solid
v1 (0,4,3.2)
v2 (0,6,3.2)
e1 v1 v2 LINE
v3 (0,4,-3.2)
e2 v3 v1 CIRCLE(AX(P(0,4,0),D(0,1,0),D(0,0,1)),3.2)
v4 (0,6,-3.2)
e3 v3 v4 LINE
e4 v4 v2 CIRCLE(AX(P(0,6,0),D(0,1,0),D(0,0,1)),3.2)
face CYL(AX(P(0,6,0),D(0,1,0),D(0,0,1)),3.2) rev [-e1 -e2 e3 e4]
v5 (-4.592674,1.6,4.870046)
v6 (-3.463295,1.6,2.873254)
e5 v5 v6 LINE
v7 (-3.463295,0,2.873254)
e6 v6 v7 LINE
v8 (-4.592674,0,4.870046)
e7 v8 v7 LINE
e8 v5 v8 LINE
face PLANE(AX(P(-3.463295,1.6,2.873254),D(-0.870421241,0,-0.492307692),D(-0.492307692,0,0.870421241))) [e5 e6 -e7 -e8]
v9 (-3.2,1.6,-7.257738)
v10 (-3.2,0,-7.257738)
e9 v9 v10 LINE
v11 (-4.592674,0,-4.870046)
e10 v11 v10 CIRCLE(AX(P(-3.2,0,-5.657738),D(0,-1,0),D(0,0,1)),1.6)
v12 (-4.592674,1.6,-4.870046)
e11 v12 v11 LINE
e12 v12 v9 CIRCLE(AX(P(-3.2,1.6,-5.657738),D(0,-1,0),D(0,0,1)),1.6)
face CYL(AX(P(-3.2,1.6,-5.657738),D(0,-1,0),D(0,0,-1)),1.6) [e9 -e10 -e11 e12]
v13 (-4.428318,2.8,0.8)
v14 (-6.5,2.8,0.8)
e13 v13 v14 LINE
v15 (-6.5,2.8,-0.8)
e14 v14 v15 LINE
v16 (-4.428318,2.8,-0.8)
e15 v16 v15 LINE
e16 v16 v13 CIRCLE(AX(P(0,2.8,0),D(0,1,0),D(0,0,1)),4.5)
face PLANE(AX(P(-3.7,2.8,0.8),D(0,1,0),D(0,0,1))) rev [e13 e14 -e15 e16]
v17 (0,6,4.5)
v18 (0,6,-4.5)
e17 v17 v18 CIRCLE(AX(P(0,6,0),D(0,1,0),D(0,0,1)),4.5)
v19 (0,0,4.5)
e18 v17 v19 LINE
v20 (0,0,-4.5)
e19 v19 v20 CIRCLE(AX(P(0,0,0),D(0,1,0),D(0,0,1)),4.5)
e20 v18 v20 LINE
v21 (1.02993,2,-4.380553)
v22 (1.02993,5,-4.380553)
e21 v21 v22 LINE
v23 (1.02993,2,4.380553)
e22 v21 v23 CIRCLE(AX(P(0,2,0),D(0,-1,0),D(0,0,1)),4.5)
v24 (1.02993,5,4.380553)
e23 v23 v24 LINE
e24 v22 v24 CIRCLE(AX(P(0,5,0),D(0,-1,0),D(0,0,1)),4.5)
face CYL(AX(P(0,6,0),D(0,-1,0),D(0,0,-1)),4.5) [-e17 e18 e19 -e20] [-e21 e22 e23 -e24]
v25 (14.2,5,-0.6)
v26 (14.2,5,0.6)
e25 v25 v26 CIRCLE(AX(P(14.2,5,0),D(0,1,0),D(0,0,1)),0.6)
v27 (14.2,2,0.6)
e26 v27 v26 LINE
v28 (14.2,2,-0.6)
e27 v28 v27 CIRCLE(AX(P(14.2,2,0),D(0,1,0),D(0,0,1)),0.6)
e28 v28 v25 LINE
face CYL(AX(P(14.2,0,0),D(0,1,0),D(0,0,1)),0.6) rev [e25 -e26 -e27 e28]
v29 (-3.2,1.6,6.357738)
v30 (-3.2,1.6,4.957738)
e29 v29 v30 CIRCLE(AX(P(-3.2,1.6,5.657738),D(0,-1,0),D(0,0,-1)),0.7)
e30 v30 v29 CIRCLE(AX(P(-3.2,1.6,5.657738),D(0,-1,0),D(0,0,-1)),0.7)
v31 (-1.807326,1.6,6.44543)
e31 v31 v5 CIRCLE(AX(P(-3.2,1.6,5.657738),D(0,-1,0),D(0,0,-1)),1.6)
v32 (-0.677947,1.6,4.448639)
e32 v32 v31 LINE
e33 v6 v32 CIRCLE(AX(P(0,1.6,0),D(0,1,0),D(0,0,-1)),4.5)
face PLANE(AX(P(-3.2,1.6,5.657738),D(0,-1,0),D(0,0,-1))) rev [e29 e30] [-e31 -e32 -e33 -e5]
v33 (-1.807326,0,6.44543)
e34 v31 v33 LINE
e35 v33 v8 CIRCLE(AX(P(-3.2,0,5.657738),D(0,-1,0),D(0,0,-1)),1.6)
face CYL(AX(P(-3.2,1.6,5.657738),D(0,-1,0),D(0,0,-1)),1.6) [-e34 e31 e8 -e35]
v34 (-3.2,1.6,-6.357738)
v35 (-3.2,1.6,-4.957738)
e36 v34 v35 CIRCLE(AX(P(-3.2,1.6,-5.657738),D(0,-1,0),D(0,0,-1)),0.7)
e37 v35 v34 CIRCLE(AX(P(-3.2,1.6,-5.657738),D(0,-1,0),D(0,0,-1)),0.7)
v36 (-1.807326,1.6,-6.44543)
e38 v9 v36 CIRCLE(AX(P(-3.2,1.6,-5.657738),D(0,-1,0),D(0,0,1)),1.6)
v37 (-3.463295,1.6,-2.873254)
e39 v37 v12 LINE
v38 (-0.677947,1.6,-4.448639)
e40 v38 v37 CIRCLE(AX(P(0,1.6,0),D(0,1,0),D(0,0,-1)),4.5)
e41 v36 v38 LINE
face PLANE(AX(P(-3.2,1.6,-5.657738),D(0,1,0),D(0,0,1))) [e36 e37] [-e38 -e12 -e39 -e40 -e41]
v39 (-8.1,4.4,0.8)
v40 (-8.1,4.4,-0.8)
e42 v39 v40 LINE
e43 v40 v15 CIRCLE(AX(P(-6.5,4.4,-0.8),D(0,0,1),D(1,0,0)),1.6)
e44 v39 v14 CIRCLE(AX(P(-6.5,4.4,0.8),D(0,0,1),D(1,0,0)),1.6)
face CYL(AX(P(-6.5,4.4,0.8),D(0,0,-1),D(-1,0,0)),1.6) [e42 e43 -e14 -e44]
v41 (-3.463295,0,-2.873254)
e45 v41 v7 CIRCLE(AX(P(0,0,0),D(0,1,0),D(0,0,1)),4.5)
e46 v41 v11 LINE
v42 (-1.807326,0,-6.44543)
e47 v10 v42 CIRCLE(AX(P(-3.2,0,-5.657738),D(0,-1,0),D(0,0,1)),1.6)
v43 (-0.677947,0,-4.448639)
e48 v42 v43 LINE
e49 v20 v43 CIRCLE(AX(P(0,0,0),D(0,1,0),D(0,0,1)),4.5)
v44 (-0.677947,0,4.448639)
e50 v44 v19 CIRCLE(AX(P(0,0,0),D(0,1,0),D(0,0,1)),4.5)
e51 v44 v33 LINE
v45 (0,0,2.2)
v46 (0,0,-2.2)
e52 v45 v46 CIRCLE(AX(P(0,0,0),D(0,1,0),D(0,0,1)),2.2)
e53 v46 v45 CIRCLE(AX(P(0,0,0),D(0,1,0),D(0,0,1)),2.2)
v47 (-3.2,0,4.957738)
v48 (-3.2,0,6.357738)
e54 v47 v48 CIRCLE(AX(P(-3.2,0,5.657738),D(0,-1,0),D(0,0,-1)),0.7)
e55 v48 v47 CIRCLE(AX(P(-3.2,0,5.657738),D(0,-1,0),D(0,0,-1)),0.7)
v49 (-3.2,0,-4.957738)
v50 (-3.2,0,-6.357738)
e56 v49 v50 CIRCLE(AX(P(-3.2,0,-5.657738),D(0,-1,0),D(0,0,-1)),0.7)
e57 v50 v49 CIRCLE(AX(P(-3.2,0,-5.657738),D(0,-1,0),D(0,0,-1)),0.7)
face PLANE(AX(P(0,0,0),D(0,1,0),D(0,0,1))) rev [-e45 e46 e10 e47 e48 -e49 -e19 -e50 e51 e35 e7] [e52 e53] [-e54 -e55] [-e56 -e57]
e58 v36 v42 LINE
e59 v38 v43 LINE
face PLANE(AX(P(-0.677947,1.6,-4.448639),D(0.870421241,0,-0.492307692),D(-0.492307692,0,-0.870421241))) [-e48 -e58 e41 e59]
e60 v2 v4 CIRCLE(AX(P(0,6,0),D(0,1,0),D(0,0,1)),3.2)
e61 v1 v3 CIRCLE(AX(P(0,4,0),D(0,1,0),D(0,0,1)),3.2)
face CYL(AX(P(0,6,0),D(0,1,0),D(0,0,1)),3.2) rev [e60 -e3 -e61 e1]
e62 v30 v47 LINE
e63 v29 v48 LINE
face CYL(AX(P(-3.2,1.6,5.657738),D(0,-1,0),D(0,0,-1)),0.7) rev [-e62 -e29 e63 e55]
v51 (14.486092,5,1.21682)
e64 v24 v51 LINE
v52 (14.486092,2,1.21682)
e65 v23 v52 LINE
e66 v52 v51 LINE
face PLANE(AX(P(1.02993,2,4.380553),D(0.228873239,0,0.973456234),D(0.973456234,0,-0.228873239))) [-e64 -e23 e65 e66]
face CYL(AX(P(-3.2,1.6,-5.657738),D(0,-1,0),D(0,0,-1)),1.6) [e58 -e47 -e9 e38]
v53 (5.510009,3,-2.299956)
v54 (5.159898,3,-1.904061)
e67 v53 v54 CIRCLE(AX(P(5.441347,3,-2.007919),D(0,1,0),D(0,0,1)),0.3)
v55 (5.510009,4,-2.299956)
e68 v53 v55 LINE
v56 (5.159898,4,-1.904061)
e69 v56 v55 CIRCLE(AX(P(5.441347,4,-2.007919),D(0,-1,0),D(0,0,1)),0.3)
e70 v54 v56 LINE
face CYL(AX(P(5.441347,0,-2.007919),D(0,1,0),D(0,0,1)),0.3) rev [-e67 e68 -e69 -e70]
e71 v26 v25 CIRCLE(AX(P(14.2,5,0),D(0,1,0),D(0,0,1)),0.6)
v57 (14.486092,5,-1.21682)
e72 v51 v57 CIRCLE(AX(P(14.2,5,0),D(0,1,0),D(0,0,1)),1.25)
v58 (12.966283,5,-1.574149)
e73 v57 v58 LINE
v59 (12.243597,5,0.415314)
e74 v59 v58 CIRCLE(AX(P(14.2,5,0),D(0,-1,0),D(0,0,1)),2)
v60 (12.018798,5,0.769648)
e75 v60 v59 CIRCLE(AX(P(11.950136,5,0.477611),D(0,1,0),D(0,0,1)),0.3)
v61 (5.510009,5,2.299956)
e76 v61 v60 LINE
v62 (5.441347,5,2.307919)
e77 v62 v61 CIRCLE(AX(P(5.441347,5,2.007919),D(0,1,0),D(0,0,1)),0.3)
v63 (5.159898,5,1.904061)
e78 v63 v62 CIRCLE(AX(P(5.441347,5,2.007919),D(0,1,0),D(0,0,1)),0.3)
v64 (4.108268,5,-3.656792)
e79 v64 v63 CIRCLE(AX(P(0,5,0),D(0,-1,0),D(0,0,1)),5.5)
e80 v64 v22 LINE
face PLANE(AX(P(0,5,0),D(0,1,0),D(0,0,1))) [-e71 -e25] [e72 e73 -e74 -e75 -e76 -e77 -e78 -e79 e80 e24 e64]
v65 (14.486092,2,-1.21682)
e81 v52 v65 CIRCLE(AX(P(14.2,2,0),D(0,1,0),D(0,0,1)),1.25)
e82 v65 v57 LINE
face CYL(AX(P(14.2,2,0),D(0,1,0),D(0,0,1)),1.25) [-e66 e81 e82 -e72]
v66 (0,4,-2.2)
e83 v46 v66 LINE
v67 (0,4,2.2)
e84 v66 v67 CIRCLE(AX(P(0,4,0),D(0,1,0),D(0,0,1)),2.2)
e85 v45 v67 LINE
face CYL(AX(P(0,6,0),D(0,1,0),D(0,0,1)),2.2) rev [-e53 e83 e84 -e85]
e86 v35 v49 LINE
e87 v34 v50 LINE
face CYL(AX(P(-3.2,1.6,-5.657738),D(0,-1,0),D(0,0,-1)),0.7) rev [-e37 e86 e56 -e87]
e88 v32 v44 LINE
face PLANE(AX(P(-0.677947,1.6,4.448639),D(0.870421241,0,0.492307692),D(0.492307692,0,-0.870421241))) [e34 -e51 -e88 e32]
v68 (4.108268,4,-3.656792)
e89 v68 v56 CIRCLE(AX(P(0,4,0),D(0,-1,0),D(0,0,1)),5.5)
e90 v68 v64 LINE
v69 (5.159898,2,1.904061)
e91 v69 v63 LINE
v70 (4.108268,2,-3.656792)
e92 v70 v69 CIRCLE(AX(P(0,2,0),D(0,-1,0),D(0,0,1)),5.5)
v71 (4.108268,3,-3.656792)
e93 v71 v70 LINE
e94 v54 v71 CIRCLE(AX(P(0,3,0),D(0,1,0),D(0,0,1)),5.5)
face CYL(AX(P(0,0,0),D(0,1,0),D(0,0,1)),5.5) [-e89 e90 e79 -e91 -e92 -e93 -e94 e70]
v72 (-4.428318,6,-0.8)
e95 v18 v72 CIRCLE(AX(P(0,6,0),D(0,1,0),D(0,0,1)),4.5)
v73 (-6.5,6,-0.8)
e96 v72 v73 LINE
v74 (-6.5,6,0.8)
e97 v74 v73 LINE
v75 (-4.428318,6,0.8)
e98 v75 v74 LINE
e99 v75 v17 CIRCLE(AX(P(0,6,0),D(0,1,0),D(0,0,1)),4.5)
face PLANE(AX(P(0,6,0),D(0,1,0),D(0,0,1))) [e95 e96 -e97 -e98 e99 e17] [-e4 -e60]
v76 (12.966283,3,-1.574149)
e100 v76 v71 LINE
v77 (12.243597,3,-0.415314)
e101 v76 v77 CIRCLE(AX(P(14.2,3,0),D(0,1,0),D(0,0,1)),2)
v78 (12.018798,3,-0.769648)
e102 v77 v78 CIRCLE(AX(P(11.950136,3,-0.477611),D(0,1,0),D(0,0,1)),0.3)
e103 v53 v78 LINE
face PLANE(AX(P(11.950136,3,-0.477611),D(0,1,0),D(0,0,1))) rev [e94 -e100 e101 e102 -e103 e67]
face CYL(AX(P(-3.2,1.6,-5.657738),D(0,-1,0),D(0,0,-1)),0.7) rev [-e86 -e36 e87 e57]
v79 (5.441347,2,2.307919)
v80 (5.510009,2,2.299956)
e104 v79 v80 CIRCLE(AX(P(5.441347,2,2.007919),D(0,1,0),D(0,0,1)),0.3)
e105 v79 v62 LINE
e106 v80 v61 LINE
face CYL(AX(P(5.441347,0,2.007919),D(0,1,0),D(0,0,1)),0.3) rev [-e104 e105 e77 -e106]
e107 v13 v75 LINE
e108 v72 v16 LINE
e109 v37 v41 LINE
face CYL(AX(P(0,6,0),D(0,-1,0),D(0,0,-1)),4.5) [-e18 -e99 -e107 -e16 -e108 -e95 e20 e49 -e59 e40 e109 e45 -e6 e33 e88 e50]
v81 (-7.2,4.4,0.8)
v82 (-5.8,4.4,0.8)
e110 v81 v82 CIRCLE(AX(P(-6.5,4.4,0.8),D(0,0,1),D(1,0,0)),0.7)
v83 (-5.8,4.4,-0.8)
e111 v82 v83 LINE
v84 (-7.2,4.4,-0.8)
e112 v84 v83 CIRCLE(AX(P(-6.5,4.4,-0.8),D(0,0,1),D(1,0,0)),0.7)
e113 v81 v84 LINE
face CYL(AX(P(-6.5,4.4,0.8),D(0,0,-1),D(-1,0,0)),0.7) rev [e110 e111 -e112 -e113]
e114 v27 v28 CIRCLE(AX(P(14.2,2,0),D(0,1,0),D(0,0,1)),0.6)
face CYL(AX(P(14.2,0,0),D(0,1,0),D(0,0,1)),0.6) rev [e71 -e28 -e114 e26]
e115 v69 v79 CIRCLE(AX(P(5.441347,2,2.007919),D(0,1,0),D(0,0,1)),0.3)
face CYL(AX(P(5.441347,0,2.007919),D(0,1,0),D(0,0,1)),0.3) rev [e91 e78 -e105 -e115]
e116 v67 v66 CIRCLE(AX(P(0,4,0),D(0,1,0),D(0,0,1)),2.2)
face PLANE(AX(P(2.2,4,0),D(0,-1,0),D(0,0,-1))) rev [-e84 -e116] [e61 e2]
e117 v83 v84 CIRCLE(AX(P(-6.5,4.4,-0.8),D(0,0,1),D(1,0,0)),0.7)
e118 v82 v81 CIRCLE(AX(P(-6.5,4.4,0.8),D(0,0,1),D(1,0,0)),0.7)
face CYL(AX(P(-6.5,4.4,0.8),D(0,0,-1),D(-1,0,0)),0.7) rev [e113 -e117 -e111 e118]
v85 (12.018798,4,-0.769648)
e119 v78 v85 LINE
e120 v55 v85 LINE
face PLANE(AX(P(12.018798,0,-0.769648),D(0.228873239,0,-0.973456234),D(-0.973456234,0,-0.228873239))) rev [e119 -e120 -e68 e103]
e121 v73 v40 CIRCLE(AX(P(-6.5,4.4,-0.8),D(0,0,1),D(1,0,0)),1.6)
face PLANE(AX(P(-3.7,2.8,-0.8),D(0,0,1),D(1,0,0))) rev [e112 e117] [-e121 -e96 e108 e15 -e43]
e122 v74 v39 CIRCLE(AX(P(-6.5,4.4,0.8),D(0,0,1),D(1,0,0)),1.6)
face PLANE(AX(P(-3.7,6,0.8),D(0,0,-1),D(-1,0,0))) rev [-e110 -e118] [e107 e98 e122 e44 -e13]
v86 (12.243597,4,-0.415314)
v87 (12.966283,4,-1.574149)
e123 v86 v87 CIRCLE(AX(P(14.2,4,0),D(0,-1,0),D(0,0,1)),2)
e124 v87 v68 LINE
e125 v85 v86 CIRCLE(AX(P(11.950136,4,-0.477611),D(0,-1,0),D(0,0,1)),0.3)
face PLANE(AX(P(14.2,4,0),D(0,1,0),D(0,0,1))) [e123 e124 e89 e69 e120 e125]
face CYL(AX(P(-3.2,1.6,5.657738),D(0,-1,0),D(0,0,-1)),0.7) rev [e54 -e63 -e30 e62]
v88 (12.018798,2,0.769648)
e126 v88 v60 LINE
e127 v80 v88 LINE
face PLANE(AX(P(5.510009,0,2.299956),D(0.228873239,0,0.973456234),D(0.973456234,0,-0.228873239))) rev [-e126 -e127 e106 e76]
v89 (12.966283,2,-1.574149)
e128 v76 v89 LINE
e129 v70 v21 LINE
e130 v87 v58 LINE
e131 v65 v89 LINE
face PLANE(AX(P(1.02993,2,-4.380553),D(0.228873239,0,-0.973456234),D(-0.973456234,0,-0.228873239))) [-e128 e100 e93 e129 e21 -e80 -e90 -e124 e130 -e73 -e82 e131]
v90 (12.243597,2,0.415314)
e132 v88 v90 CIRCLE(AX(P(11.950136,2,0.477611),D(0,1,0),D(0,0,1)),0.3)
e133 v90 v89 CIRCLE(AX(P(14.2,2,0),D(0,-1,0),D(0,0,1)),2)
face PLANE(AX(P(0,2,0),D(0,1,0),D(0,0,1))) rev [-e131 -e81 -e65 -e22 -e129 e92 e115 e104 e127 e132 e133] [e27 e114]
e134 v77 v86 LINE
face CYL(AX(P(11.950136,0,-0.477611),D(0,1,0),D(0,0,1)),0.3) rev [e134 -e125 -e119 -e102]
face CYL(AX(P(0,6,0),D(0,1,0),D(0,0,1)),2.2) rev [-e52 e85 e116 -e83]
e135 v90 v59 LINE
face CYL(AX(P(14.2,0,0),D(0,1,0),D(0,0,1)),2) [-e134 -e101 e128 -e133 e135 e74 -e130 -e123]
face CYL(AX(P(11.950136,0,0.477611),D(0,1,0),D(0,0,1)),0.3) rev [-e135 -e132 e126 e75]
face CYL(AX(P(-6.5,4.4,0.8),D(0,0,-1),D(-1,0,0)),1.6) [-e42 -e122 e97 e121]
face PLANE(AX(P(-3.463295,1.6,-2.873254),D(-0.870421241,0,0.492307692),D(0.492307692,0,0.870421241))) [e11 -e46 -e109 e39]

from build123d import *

# Parameters (mm, degrees)
HUB_PROFILE_SKETCH_R           = 4.5
HUB_CYLINDER_DEPTH             = 6
ARM_START                      = -4
ARM_DEPTH                      = 3
FLAT_EAR_PROFILE_SKETCH_R      = 0.7
FLAT_MOUNTING_EAR_DEPTH        = 1.6
UPRIGHT_EAR_PROFILE_SKETCH_R   = 0.7
UPRIGHT_MOUNTING_EAR_DEPTH     = 0.8
UPRIGHT_EAR_EXTENSION_SKETCH_W = 1.6
UPRIGHT_EAR_EXTENSION_SKETCH_H = 3.2
UPRIGHT_EAR_EXTENSION_DEPTH    = 0.8
HUB_BORE_CBORE_4_4_D           = 4.4
HUB_BORE_CBORE_4_4_DEPTH       = 100
HUB_BORE_CBORE_4_4_CBORE_D     = 6.4
HUB_BORE_CBORE_4_4_CBORE_DEPTH = 2
ARM_FRAME_CUT_DEPTH            = 18.786996987
ARM_FRAME_CUT_DEPTH_BACK       = 18.786996987
ARM_FRAME_CUT_SKETCH_R         = 0.6
ARM_START_2                    = -1
ARM_WINDOW_CUT_A_DEPTH         = 1
ARM_START_3                    = -3
ARM_WINDOW_CUT_B_DEPTH         = 1


with BuildPart() as part:
    # Hub Profile Sketch → Hub Cylinder (new body)
    with BuildSketch(Plane(origin=(0, 0, 0), x_dir=(1, 0, 0), z_dir=(0, 1, 0))):
        with Locations(Location((0, 0, 0), (0, 0, 270))):
            Circle(HUB_PROFILE_SKETCH_R)
    extrude(amount=HUB_CYLINDER_DEPTH)

    # Arm Profile Sketch → Arm (add)
    with BuildSketch(Plane(origin=(0, 6, 0), x_dir=(1, 0, 0), z_dir=(0, 1, 0)).offset(ARM_START)):
        with BuildLine():
            Line((1.029929577, 4.380553055), (14.486091549, 1.216820293))
            ThreePointArc((14.486091549, 1.216820293), (15.45, 0), (14.486091549, -1.216820293))
            Line((14.486091549, -1.216820293), (1.029929577, -4.380553055))
            ThreePointArc((1.029929577, -4.380553055), (4.5, 0), (1.029929577, 4.380553055))
        make_face()
    extrude(amount=ARM_DEPTH)

    # Flat Ear Profile Sketch → Flat Mounting Ear (add)
    # profile 1 of 2: a face of its own
    with BuildSketch(Plane.XZ):
        with BuildLine():
            Line((-0.677946652, 4.448638931), (-1.807326015, 6.445430372))
            ThreePointArc((-1.807326015, 6.445430372), (-3.987692308, 7.050412049), (-4.592673985, 4.870045756))
            Line((-4.592673985, 4.870045756), (-3.463294622, 2.873254315))
            ThreePointArc((-3.463294622, 2.873254315), (-2.215384615, 3.916895583), (-0.677946652, 4.448638931))
        make_face()
        with Locations(Location((-3.2, 5.657738064, 0), (0, 0, 270))):
            Circle(FLAT_EAR_PROFILE_SKETCH_R, mode=Mode.SUBTRACT)
    # profile 2 of 2: a face of its own
    with BuildSketch(Plane.XZ):
        with BuildLine():
            Line((-0.677946652, -4.448638931), (-1.807326015, -6.445430372))
            ThreePointArc((-1.807326015, -6.445430372), (-3.987692308, -7.050412049), (-4.592673985, -4.870045756))
            Line((-4.592673985, -4.870045756), (-3.463294622, -2.873254315))
            ThreePointArc((-3.463294622, -2.873254315), (-2.215384615, -3.916895583), (-0.677946652, -4.448638931))
        make_face()
        with Locations(Location((-3.2, -5.657738064, 0), (0, 0, 270))):
            Circle(FLAT_EAR_PROFILE_SKETCH_R, mode=Mode.SUBTRACT)
    extrude(amount=-FLAT_MOUNTING_EAR_DEPTH)



with BuildPart() as body_2:
    # Upright Ear Profile Sketch → Upright Mounting Ear (new, symmetric)
    with BuildSketch(Plane.XY):
        with BuildLine():
            Line((-4.5, 6), (-6.5, 6))
            ThreePointArc((-6.5, 6), (-8.1, 4.4), (-6.5, 2.8))
            Line((-6.5, 2.8), (-4.5, 2.8))
            Line((-4.5, 2.8), (-4.5, 6))
        make_face()
        with Locations((-6.5, 4.4)):
            Circle(UPRIGHT_EAR_PROFILE_SKETCH_R, mode=Mode.SUBTRACT)
    extrude(amount=UPRIGHT_MOUNTING_EAR_DEPTH, both=True)


with BuildPart() as part_1:
    add(part.part)

    add(body_2.part)  # Upright Ear Extension merges body 2
    # Upright Ear Extension Sketch → Upright Ear Extension (add, symmetric)
    with BuildSketch(Plane(origin=(-4.5, 0, 0), x_dir=(0, 0, -1), z_dir=(1, 0, 0))):
        with Locations((0, 4.4)):
            Rectangle(UPRIGHT_EAR_EXTENSION_SKETCH_W, UPRIGHT_EAR_EXTENSION_SKETCH_H)
    extrude(amount=UPRIGHT_EAR_EXTENSION_DEPTH, both=True)

    # Hub Bore CBore _4.4
    with Locations(Plane(origin=(0, 6, 0), x_dir=(1, 0, 0), z_dir=(0, 1, 0))):
        with Locations((0, 0)):
            CounterBoreHole(HUB_BORE_CBORE_4_4_D / 2, HUB_BORE_CBORE_4_4_CBORE_D / 2, HUB_BORE_CBORE_4_4_CBORE_DEPTH, depth=HUB_BORE_CBORE_4_4_DEPTH)

    # Arm Frame Cut Sketch → Arm Frame Cut (cut, two sides: drawn at the far end of the back side and taken through both)
    with BuildSketch(Plane(origin=(0, 5, 0), x_dir=(1, 0, 0), z_dir=(0, 1, 0)).offset(-ARM_FRAME_CUT_DEPTH_BACK)):
        with Locations(Location((14.2, 0, 0), (0, 0, 270))):
            Circle(ARM_FRAME_CUT_SKETCH_R)
        with BuildLine():
            Line((12.018798086, 0.769648107), (5.510009379, 2.299955792))
            ThreePointArc((5.510009379, 2.299955792), (5.216619254, 2.20665809), (5.159898403, 1.904061046))
            ThreePointArc((5.159898403, 1.904061046), (5.5, 0), (5.159898403, -1.904061046))
            ThreePointArc((5.159898403, -1.904061046), (5.216619254, -2.20665809), (5.510009379, -2.299955792))
            Line((5.510009379, -2.299955792), (12.018798086, -0.769648107))
            ThreePointArc((12.018798086, -0.769648107), (12.203456694, -0.638324285), (12.243596621, -0.415314119))
            ThreePointArc((12.243596621, -0.415314119), (12.2, 0), (12.243596621, 0.415314119))
            ThreePointArc((12.243596621, 0.415314119), (12.203456694, 0.638324285), (12.018798086, 0.769648107))
        make_face()
    extrude(amount=ARM_FRAME_CUT_DEPTH + ARM_FRAME_CUT_DEPTH_BACK, mode=Mode.SUBTRACT)

    # Arm Window Sketch → Arm Window Cut A (cut)
    with BuildSketch(Plane(origin=(0, 5, 0), x_dir=(1, 0, 0), z_dir=(0, 1, 0)).offset(ARM_START_2)):
        with BuildLine():
            Line((12.96628349, 1.574148524), (4.108268481, 3.656792323))
            ThreePointArc((4.108268481, 3.656792323), (4.716221589, 2.829709158), (5.159898403, 1.904061046))
            ThreePointArc((5.159898403, 1.904061046), (5.216619254, 2.20665809), (5.510009379, 2.299955792))
            Line((5.510009379, 2.299955792), (12.018798086, 0.769648107))
            ThreePointArc((12.018798086, 0.769648107), (12.203456694, 0.638324285), (12.243596621, 0.415314119))
            ThreePointArc((12.243596621, 0.415314119), (12.502961249, 1.058328625), (12.96628349, 1.574148524))
        make_face()
    extrude(amount=ARM_WINDOW_CUT_A_DEPTH, mode=Mode.SUBTRACT)

    # Sketch12_2 → Arm Window Cut B (cut)
    with BuildSketch(Plane(origin=(0, 5, 0), x_dir=(1, 0, 0), z_dir=(0, 1, 0)).offset(ARM_START_3)):
        with BuildLine():
            Line((12.96628349, 1.574148524), (4.108268481, 3.656792323))
            ThreePointArc((4.108268481, 3.656792323), (4.716221589, 2.829709158), (5.159898403, 1.904061046))
            ThreePointArc((5.159898403, 1.904061046), (5.216619254, 2.20665809), (5.510009379, 2.299955792))
            Line((5.510009379, 2.299955792), (12.018798086, 0.769648107))
            ThreePointArc((12.018798086, 0.769648107), (12.203456694, 0.638324285), (12.243596621, 0.415314119))
            ThreePointArc((12.243596621, 0.415314119), (12.502961249, 1.058328625), (12.96628349, 1.574148524))
        make_face()
    extrude(amount=ARM_WINDOW_CUT_B_DEPTH, mode=Mode.SUBTRACT)


solid = part_1.part
